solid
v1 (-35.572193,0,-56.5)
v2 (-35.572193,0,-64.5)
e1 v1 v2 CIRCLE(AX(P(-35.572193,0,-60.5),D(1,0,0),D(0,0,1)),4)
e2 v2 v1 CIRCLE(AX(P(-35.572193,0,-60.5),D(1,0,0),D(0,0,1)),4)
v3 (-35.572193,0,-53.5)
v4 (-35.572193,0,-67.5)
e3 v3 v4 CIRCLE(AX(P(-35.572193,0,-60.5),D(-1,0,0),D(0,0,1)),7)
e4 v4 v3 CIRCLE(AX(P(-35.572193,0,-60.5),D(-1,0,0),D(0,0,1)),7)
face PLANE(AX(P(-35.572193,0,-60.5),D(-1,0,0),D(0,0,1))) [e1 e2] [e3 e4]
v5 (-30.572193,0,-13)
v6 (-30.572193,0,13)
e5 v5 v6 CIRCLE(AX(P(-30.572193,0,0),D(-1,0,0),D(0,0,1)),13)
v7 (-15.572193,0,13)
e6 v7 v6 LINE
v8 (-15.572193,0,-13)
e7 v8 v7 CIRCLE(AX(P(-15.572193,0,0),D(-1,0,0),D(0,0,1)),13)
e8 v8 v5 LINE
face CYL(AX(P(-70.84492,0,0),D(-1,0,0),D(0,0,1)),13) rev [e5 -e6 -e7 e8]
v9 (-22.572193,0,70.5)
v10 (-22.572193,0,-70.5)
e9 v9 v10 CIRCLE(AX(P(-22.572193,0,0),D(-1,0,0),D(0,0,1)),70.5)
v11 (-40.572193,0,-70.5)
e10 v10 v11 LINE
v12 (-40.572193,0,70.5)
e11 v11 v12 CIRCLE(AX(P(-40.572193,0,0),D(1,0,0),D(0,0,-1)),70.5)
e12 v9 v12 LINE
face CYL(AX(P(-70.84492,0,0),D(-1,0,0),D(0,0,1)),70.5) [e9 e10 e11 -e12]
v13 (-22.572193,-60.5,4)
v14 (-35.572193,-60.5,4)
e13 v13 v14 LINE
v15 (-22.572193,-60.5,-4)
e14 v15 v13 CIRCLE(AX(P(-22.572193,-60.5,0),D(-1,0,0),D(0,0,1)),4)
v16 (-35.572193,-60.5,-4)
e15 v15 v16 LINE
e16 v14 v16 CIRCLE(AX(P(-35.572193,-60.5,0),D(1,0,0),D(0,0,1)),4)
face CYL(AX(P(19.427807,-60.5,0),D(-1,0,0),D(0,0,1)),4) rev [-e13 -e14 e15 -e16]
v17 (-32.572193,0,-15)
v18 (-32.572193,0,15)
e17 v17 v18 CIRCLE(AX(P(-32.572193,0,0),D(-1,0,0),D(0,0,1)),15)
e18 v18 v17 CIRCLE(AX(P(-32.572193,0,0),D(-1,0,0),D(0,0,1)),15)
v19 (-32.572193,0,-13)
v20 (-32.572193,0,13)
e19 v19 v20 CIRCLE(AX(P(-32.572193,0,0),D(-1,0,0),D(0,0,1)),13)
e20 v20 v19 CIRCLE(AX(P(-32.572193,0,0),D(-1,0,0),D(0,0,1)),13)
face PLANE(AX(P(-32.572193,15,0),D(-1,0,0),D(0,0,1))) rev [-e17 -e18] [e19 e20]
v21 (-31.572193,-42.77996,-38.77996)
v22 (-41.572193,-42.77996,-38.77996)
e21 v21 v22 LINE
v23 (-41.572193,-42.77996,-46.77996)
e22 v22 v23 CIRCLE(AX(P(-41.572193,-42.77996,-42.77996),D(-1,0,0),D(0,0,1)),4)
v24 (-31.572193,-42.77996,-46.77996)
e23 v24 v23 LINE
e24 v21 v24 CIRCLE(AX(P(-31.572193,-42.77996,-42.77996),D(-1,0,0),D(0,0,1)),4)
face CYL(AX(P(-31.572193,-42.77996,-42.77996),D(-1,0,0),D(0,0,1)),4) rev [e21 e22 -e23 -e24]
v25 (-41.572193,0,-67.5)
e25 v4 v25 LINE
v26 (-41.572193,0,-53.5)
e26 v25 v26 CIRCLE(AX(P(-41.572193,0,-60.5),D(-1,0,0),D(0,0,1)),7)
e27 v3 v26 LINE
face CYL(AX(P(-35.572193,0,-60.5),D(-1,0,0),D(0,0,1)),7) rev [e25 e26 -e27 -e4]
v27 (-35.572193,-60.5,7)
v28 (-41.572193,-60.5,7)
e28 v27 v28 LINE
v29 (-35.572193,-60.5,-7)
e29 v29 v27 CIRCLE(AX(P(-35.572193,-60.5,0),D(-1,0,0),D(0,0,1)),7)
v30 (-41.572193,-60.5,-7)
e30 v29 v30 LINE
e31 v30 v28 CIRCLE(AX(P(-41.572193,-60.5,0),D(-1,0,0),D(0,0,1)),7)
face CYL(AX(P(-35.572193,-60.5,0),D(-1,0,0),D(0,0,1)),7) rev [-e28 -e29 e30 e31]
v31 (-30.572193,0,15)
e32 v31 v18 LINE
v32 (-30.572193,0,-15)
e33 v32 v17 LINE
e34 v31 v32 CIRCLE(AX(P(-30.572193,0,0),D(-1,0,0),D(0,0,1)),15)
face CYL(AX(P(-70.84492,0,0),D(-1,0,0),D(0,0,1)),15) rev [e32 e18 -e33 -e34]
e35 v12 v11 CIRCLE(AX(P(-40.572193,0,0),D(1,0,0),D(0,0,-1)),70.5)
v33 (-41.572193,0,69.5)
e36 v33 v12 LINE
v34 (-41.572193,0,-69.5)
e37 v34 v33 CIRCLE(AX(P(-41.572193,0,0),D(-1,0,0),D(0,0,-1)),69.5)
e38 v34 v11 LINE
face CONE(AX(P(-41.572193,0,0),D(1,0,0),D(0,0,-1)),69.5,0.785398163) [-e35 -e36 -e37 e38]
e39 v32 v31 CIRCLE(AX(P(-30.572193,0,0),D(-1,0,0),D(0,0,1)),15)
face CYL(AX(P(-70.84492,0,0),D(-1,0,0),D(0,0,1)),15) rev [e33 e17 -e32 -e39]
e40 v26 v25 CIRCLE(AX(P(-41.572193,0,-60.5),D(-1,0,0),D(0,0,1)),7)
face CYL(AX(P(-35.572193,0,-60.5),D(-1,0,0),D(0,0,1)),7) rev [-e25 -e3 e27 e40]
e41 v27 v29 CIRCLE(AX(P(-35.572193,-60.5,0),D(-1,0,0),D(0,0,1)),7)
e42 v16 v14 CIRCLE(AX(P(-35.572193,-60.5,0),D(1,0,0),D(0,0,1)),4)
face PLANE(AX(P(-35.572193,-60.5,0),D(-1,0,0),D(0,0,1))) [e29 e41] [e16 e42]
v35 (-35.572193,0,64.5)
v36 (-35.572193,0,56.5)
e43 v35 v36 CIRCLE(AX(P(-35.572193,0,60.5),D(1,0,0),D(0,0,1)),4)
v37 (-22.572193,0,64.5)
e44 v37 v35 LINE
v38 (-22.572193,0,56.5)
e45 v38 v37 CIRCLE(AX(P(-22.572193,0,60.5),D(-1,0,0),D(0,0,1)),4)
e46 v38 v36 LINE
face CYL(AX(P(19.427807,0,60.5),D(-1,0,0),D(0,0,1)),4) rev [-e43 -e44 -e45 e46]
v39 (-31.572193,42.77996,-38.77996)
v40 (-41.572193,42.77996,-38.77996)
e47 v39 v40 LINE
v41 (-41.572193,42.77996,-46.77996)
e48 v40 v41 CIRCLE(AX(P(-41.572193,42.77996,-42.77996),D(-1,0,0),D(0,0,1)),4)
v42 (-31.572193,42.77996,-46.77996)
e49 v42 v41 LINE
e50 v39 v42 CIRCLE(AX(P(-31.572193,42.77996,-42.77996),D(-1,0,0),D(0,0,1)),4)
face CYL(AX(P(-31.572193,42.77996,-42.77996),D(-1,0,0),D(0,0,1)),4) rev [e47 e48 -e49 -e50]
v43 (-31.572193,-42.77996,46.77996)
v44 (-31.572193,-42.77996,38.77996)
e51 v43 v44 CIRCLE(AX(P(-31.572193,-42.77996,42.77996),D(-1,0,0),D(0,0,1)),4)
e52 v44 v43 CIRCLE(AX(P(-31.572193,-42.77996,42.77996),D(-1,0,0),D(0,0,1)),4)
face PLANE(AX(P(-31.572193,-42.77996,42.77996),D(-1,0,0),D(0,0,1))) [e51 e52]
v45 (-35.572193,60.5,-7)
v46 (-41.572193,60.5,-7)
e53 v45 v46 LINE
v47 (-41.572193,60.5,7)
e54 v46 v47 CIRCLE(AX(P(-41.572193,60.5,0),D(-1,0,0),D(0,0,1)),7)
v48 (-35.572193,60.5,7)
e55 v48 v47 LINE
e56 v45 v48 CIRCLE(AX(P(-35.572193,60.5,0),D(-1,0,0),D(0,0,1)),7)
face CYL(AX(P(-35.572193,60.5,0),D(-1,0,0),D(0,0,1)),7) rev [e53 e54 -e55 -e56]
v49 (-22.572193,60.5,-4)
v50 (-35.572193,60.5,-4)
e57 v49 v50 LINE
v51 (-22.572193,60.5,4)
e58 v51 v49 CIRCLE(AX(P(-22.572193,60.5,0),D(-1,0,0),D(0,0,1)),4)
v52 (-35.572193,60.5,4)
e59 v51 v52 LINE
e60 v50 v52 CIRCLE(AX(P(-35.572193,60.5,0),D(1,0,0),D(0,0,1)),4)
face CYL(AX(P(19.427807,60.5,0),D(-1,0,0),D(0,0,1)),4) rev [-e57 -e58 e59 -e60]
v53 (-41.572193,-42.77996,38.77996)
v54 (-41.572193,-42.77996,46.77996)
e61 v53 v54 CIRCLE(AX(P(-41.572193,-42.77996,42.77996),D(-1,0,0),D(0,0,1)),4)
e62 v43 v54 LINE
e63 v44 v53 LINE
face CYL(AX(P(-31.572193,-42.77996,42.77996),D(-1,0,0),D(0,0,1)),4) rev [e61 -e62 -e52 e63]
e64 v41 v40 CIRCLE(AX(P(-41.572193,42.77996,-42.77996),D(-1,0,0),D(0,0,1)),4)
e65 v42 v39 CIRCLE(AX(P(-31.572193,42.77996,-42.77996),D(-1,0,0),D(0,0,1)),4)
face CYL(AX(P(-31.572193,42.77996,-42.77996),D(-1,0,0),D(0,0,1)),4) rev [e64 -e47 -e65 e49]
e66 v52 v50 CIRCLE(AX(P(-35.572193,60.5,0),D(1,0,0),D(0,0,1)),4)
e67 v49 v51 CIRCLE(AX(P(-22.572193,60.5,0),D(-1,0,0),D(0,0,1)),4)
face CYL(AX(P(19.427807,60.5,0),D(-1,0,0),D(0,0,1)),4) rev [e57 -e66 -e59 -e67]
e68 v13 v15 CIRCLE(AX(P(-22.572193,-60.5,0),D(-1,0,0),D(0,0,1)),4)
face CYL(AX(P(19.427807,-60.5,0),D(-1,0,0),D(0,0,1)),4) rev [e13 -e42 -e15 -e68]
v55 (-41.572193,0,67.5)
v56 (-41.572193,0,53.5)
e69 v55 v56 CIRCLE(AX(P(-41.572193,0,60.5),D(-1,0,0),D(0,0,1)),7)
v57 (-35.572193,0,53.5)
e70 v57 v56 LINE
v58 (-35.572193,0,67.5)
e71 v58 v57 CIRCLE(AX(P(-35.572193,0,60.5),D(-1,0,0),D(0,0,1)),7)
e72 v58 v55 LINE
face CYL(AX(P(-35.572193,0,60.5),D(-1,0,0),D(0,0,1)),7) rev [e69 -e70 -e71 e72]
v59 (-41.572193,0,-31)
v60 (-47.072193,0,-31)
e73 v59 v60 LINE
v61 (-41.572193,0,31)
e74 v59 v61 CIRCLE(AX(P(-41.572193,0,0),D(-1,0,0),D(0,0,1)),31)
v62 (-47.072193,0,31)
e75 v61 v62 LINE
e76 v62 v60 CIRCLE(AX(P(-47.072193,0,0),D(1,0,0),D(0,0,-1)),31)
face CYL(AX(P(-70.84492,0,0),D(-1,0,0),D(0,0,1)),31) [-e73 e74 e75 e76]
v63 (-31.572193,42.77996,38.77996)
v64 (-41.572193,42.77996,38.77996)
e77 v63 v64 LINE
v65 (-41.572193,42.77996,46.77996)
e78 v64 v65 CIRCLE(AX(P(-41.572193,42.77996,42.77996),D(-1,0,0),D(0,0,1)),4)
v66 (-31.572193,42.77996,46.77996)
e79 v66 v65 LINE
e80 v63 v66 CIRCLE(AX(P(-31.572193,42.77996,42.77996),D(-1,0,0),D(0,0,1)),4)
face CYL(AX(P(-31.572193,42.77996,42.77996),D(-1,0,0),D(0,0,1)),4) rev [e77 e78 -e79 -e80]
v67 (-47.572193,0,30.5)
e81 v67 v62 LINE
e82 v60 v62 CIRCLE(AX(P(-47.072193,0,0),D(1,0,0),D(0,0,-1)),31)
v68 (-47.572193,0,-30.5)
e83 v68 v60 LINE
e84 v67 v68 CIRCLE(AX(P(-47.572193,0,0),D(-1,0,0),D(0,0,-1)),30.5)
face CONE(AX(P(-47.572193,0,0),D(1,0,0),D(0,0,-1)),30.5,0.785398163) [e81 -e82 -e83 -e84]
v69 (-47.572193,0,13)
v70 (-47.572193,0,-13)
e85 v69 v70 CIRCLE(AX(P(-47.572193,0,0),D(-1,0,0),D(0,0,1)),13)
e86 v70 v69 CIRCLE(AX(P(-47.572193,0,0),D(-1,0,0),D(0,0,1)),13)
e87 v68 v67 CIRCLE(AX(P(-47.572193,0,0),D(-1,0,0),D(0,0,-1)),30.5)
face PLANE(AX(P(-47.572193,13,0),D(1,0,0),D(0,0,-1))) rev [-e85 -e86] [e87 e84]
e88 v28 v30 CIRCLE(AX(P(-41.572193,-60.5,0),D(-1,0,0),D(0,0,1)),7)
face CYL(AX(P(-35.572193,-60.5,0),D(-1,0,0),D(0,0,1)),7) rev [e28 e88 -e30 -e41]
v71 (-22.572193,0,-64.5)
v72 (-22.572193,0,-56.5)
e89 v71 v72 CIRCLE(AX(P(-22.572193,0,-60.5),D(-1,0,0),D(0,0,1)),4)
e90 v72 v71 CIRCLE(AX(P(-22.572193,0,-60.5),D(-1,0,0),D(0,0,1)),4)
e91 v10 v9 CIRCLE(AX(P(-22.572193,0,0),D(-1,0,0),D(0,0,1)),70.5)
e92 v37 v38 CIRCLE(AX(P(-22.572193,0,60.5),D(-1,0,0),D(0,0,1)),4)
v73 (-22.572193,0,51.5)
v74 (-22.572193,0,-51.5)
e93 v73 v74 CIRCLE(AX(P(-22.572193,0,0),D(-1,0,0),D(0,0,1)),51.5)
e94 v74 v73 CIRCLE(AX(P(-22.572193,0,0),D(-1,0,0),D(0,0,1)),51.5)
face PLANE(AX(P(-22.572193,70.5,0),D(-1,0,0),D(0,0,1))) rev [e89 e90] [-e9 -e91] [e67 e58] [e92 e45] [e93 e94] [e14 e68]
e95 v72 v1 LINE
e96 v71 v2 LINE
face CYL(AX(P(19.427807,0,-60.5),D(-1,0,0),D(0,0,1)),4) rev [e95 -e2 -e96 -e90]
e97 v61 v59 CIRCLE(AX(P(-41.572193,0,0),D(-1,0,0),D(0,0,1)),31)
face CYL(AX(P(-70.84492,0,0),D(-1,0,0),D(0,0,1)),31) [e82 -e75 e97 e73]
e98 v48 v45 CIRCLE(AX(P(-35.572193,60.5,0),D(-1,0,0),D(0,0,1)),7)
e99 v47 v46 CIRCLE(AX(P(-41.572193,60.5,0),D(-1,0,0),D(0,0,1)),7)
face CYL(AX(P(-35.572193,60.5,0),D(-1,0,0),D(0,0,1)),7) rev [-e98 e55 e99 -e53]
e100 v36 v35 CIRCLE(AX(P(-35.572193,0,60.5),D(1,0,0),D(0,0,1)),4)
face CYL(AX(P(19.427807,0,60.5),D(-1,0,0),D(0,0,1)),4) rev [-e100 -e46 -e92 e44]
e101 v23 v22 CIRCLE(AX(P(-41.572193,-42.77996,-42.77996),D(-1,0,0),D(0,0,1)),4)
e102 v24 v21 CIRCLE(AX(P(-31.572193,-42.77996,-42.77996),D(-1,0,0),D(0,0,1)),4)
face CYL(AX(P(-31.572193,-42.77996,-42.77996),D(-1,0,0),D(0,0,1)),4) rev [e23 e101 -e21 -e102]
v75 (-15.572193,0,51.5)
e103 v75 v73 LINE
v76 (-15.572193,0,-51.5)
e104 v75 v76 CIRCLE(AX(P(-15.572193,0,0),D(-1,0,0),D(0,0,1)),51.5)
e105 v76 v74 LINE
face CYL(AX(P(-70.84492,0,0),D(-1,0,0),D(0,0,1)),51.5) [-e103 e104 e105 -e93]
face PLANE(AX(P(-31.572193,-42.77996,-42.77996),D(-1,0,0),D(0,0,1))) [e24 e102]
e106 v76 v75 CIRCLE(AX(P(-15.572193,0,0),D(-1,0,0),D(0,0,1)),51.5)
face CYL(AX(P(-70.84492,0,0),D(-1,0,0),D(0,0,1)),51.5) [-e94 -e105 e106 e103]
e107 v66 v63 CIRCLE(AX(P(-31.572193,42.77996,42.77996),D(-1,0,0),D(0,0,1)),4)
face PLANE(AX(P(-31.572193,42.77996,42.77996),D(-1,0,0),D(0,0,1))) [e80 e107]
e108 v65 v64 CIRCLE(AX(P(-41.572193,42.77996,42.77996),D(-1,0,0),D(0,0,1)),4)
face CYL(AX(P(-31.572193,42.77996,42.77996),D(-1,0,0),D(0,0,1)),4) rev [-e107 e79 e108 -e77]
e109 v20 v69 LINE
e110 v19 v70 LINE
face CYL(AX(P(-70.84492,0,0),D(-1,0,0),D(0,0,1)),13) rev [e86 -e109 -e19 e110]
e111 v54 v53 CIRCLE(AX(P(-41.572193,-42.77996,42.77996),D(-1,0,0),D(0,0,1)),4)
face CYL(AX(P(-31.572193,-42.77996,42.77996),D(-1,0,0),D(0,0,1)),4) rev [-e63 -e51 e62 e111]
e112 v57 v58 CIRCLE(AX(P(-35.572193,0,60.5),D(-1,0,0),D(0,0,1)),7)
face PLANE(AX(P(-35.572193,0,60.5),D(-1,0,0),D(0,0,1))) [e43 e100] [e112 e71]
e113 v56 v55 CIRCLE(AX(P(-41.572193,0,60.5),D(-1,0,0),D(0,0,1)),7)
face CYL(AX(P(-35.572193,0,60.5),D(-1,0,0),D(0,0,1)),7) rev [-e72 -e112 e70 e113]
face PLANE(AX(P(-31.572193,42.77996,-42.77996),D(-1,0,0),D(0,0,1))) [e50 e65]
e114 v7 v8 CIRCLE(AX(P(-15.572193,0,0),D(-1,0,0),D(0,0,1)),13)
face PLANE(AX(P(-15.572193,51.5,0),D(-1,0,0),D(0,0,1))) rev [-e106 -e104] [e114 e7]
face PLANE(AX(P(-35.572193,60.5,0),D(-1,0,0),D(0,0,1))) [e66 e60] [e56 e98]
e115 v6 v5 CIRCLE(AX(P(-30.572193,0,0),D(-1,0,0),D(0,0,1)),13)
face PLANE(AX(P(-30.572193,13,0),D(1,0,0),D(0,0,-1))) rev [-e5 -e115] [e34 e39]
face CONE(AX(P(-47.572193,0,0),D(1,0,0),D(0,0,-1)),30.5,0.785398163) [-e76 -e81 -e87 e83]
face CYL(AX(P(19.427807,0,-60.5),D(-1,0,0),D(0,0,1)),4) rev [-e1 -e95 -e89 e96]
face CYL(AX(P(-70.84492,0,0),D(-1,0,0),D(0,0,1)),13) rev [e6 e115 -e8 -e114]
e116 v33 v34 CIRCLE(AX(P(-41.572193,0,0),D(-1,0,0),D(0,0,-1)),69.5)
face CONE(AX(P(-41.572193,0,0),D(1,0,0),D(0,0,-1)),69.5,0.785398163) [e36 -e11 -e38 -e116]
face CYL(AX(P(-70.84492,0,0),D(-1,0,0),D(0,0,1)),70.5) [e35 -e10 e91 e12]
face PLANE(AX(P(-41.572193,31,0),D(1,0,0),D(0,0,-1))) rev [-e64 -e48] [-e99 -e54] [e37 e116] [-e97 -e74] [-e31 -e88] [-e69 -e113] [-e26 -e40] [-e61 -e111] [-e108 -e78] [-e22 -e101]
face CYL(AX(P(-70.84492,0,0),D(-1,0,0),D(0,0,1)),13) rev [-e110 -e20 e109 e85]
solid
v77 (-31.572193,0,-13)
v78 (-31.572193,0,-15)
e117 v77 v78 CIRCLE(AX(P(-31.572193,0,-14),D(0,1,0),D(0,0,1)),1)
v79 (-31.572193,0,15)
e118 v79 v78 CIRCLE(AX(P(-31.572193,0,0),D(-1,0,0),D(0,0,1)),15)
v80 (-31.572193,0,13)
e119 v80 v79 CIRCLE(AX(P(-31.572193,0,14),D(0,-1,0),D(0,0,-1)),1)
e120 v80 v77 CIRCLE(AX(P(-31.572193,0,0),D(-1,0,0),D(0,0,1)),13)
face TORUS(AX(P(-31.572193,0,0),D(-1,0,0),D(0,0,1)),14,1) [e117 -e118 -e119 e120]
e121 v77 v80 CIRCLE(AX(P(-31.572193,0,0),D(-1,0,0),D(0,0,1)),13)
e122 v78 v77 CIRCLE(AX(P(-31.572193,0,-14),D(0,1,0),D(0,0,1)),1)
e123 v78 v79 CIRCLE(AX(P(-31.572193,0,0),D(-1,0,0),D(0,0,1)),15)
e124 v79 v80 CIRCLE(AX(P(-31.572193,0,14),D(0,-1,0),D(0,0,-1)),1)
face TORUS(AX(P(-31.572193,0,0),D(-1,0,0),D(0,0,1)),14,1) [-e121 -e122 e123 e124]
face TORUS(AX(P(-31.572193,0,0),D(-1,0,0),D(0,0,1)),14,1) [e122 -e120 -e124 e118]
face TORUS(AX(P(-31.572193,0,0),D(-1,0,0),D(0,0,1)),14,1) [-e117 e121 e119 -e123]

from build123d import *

# Parameters (mm, degrees)
CHAMFER1_SIZE      = 0.5
CHAMFER2_SIZE      = 1
SKETCH2_R          = 4
CUT_EXTRUDE2_DEPTH = 61
SKETCH6_R          = 7
CUT_EXTRUDE3_DEPTH = 6
SKETCH8_R          = 1
SKETCH9_R          = 4
CUT_EXTRUDE4_DEPTH = 10


with BuildPart() as part:
    # Sketch1 → Revolve1 (revolve)
    with BuildSketch(Plane.XY, mode=Mode.PRIVATE) as revolve1_sk:
        Polygon((-47.572192513, 13), (-47.572192513, 31), (-41.572192513, 31), (-41.572192513, 70.5), (-22.572192513, 70.5), (-22.572192513, 51.5), (-15.572192513, 51.5), (-15.572192513, 13), (-30.572192513, 13), (-30.572192513, 15), (-32.572192513, 15), (-32.572192513, 13), align=None)
    revolve(revolve1_sk.sketch.rotate(Axis((-70.844919786, 0, 0), (1, 0, 0)), 90), axis=Axis((-70.844919786, 0, 0), (1, 0, 0)))

    # Chamfer1
    chamfer1_edges = [part.edges().sort_by_distance(p)[0] for p in [
        (-47.572192513, 0, -31),
    ]]
    chamfer(chamfer1_edges, length=CHAMFER1_SIZE)

    # Chamfer2
    chamfer2_edges = [part.edges().sort_by_distance(p)[0] for p in [
        (-41.572192513, 0, -70.5),
    ]]
    chamfer(chamfer2_edges, length=CHAMFER2_SIZE)

    # Sketch2 → Cut-Extrude2 (cut)
    with BuildSketch(Plane.ZY.offset(41.572192513)):
        with Locations((0, -60.5)):
            Circle(SKETCH2_R)
        with Locations((-60.5, 0)):
            Circle(SKETCH2_R)
        with Locations((0, 60.5)):
            Circle(SKETCH2_R)
        with Locations((60.5, 0)):
            Circle(SKETCH2_R)
    extrude(amount=-CUT_EXTRUDE2_DEPTH, mode=Mode.SUBTRACT)

    # Sketch6 → Cut-Extrude3 (cut)
    with BuildSketch(Plane.ZY.offset(41.572192513)):
        with Locations((0, -60.5)):
            Circle(SKETCH6_R)
        with Locations((-60.5, 0)):
            Circle(SKETCH6_R)
        with Locations((60.5, 0)):
            Circle(SKETCH6_R)
        with Locations((0, 60.5)):
            Circle(SKETCH6_R)
    extrude(amount=-CUT_EXTRUDE3_DEPTH, mode=Mode.SUBTRACT)

    # Sketch9 → Cut-Extrude4 (cut)
    with BuildSketch(Plane.ZY.offset(41.572192513)):
        with Locations((42.779960262, -42.779960262)):
            Circle(SKETCH9_R)
        with Locations((42.779960262, 42.779960262)):
            Circle(SKETCH9_R)
        with Locations((-42.779960262, -42.779960262)):
            Circle(SKETCH9_R)
        with Locations((-42.779960262, 42.779960262)):
            Circle(SKETCH9_R)
    extrude(amount=-CUT_EXTRUDE4_DEPTH, mode=Mode.SUBTRACT)


with BuildPart() as body_2:
    # Sketch8 → Revolve3 (revolve)
    with BuildSketch(Plane.XY, mode=Mode.PRIVATE) as revolve3_sk:
        with Locations((-31.572192513, 14)):
            Circle(SKETCH8_R)
    revolve(revolve3_sk.sketch.rotate(Axis((-55.043716919, 0, 0), (1, 0, 0)), 270), axis=Axis((-55.043716919, 0, 0), (1, 0, 0)))


solid = Compound([part.part, body_2.part])
